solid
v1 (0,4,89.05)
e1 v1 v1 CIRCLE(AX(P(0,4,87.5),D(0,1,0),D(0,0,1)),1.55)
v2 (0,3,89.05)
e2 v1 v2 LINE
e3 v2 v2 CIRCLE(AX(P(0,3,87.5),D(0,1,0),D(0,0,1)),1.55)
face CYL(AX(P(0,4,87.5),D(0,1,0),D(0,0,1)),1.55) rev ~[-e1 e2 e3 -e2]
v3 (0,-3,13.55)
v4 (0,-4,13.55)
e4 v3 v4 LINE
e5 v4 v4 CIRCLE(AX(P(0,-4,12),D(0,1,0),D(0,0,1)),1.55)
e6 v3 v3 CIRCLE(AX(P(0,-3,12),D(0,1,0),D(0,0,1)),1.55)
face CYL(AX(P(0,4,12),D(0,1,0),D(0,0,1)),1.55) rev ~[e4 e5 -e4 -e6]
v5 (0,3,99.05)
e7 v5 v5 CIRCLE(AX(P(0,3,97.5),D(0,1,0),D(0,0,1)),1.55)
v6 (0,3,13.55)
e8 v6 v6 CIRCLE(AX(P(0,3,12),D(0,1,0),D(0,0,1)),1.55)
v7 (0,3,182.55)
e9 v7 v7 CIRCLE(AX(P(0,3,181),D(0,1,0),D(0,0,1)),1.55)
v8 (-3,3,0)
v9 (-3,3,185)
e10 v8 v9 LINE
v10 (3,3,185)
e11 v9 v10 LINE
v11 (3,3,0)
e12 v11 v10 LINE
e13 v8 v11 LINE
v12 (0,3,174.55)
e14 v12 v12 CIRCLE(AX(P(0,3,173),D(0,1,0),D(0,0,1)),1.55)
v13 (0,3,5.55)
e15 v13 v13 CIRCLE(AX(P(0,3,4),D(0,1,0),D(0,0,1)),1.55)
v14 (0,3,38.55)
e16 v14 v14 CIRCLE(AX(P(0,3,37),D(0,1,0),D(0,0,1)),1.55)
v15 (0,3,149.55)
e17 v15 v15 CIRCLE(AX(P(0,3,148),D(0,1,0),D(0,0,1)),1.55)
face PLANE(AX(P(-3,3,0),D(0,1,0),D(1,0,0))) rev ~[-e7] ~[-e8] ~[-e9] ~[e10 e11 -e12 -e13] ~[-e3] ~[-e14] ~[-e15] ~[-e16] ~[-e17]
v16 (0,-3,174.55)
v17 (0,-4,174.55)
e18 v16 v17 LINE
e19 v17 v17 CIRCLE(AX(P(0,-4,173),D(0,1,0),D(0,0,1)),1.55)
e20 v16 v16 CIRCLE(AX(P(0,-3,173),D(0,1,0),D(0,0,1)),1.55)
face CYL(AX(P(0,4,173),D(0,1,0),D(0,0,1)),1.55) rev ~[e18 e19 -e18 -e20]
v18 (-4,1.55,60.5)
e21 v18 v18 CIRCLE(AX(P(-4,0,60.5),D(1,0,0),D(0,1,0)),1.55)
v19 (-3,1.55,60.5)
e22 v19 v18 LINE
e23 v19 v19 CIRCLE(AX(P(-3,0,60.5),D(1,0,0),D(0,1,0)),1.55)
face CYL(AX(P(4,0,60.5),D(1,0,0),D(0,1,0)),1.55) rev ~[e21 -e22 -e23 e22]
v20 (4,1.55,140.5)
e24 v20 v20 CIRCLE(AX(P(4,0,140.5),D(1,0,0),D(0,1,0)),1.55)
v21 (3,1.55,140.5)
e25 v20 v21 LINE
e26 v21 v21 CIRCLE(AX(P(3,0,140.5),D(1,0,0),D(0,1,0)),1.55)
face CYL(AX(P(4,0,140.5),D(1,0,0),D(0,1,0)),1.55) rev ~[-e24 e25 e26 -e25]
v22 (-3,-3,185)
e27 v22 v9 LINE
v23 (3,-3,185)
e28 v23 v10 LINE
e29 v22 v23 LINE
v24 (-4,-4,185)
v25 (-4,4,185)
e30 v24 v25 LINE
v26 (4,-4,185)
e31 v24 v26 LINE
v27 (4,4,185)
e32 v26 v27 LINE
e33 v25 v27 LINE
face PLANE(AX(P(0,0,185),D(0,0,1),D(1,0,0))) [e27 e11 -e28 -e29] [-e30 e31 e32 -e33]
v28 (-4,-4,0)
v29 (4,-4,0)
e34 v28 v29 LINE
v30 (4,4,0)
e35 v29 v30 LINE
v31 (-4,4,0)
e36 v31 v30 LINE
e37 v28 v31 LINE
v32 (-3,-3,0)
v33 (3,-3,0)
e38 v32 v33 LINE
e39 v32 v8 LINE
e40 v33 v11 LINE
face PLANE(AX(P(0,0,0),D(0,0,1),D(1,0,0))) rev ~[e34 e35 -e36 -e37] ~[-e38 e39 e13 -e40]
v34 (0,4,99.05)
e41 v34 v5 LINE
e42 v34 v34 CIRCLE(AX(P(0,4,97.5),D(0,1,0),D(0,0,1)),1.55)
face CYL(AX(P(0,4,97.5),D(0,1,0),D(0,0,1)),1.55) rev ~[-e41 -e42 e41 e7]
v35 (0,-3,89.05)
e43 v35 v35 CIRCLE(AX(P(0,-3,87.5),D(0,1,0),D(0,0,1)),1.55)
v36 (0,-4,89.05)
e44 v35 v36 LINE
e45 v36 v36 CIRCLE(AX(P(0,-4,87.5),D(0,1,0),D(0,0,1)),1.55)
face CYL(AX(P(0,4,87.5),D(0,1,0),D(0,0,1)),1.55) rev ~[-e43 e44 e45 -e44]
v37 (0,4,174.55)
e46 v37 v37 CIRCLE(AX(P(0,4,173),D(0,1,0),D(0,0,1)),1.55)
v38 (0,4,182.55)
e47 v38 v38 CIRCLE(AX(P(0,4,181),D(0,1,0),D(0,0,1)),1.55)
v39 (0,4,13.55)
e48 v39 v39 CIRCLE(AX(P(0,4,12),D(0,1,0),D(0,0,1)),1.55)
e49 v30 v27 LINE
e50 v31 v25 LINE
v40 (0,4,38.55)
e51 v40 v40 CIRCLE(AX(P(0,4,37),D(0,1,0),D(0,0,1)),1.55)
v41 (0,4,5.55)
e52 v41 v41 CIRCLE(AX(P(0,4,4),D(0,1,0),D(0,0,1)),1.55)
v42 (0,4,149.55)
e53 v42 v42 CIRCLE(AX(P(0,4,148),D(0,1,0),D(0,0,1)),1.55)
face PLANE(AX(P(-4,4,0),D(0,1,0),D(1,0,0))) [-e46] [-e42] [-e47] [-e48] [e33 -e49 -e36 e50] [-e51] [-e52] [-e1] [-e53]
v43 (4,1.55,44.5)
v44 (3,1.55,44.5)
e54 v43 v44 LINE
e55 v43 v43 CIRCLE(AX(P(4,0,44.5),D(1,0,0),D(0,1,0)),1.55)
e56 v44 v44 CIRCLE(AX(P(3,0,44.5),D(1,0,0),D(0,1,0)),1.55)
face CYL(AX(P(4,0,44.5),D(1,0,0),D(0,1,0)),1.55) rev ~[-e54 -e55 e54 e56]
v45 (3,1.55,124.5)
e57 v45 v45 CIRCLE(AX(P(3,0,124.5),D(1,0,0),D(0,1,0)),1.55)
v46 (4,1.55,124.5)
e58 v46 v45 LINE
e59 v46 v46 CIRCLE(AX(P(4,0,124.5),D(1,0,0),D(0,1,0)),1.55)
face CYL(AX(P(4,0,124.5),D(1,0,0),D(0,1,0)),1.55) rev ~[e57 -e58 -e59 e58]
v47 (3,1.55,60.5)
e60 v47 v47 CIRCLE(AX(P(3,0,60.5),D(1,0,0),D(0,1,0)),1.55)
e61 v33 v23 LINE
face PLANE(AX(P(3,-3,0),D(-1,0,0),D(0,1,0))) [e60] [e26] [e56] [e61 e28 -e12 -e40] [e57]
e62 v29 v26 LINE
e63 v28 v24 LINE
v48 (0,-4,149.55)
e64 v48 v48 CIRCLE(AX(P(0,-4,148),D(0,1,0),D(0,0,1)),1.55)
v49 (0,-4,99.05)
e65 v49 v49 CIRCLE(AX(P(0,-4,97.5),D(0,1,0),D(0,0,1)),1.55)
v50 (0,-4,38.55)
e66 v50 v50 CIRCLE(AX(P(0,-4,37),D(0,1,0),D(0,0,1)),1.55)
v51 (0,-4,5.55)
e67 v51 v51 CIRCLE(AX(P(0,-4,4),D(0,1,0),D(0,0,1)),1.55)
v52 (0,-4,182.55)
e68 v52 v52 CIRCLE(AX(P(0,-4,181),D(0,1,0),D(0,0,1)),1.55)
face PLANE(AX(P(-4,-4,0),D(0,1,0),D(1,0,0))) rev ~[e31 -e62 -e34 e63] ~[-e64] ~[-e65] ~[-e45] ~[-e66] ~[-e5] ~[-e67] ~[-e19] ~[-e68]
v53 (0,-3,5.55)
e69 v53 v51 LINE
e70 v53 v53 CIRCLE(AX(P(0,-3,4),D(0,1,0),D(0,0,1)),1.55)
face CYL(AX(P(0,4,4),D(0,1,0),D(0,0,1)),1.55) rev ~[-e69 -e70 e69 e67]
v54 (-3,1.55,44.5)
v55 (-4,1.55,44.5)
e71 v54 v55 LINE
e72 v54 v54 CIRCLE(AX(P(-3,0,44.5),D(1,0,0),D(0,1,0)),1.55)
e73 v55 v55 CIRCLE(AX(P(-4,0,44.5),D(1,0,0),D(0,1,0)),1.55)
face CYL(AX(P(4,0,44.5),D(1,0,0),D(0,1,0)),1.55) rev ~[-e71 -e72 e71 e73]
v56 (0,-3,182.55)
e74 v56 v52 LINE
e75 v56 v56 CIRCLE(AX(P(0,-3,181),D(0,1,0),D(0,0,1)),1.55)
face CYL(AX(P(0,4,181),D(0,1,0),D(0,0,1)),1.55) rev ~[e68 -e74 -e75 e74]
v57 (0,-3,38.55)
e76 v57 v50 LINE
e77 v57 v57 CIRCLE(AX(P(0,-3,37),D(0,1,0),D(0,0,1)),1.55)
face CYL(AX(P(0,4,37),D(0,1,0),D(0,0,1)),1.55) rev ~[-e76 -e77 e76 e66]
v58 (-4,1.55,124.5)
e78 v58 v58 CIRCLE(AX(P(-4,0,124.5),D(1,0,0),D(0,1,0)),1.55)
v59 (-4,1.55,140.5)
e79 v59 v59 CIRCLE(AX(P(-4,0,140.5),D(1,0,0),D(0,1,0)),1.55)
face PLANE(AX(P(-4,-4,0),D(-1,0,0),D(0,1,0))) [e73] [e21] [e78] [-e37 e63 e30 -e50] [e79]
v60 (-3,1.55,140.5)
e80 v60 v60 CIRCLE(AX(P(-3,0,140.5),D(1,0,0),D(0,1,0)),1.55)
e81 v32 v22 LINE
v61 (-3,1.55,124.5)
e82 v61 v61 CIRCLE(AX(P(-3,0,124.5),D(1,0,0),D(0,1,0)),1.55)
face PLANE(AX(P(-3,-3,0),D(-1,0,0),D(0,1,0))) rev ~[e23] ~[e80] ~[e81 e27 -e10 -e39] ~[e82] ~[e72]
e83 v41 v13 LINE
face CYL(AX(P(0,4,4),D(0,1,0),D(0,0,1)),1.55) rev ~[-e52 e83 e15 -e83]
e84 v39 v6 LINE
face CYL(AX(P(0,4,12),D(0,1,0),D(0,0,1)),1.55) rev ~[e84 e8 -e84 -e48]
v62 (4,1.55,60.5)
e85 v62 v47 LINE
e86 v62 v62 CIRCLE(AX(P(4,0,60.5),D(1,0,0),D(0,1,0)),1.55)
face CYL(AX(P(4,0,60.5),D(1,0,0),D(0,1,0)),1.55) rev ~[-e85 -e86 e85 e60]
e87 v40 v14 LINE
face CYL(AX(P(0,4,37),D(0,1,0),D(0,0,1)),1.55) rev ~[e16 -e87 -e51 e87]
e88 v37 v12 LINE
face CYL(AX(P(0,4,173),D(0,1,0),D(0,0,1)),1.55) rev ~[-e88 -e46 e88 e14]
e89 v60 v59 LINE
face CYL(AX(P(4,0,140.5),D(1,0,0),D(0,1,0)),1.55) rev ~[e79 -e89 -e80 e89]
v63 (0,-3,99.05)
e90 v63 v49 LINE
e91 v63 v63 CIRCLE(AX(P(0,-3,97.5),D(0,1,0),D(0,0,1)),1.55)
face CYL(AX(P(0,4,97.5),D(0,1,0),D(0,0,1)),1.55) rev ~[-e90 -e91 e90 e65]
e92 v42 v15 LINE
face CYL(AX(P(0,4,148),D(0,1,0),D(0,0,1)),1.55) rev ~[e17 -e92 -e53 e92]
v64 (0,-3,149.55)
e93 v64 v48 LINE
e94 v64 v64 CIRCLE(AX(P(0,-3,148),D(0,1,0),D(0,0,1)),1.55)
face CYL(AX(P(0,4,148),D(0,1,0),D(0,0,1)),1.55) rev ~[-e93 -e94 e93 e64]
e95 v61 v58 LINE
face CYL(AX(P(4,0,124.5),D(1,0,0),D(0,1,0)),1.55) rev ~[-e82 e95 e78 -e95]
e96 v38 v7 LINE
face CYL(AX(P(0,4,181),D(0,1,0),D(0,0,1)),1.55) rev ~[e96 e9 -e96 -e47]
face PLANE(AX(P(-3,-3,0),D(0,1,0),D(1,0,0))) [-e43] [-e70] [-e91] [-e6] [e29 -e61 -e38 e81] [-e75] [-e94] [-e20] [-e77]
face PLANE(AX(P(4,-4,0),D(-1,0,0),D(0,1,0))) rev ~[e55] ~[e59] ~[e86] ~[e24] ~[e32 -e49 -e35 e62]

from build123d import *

# Parameters (mm, degrees)
SKETCH_1_W          = 8
SKETCH_1_H          = 8
SKETCH_1_W_2        = 6
SKETCH_1_H_2        = 6
EXTRUDE_1_DEPTH     = 185
SKETCH_2_R          = 1.55
CUT_EXTRUDE_1_DEPTH = 186.216090014
SKETCH_3_R          = 1.55
CUT_EXTRUDE_2_DEPTH = 186.216090014


with BuildPart() as part:
    # 草图1 → 凸台-拉伸1 (new body)
    with BuildSketch(Plane.XY):
        Rectangle(SKETCH_1_W, SKETCH_1_H)
        Rectangle(SKETCH_1_W_2, SKETCH_1_H_2, mode=Mode.SUBTRACT)
    extrude(amount=EXTRUDE_1_DEPTH)

    # 草图2 → 切除-拉伸1 (cut, through all)
    with BuildSketch(Plane(origin=(4, 0, 0), x_dir=(0, 0, -1), z_dir=(1, 0, 0))):
        with Locations(Location((-44.5, 0, 0), (0, 0, 90))):
            Circle(SKETCH_2_R)
        with Locations(Location((-60.5, 0, 0), (0, 0, 90))):
            Circle(SKETCH_2_R)
        with Locations(Location((-124.5, 0, 0), (0, 0, 90))):
            Circle(SKETCH_2_R)
        with Locations(Location((-140.5, 0, 0), (0, 0, 90))):
            Circle(SKETCH_2_R)
    extrude(amount=-CUT_EXTRUDE_1_DEPTH, mode=Mode.SUBTRACT)

    # 草图3 → 切除-拉伸2 (cut, through all)
    with BuildSketch(Plane(origin=(0, 4, 0), x_dir=(1, 0, 0), z_dir=(0, 1, 0))):
        with Locations(Location((0, -4, 0), (0, 0, 270))):
            Circle(SKETCH_3_R)
        with Locations(Location((0, -12, 0), (0, 0, 270))):
            Circle(SKETCH_3_R)
        with Locations(Location((0, -173, 0), (0, 0, 270))):
            Circle(SKETCH_3_R)
        with Locations(Location((0, -181, 0), (0, 0, 270))):
            Circle(SKETCH_3_R)
        with Locations(Location((0, -87.5, 0), (0, 0, 270))):
            Circle(SKETCH_3_R)
        with Locations(Location((0, -97.5, 0), (0, 0, 270))):
            Circle(SKETCH_3_R)
        with Locations(Location((0, -148, 0), (0, 0, 270))):
            Circle(SKETCH_3_R)
        with Locations(Location((0, -37, 0), (0, 0, 270))):
            Circle(SKETCH_3_R)
    extrude(amount=-CUT_EXTRUDE_2_DEPTH, mode=Mode.SUBTRACT)


solid = part.part
